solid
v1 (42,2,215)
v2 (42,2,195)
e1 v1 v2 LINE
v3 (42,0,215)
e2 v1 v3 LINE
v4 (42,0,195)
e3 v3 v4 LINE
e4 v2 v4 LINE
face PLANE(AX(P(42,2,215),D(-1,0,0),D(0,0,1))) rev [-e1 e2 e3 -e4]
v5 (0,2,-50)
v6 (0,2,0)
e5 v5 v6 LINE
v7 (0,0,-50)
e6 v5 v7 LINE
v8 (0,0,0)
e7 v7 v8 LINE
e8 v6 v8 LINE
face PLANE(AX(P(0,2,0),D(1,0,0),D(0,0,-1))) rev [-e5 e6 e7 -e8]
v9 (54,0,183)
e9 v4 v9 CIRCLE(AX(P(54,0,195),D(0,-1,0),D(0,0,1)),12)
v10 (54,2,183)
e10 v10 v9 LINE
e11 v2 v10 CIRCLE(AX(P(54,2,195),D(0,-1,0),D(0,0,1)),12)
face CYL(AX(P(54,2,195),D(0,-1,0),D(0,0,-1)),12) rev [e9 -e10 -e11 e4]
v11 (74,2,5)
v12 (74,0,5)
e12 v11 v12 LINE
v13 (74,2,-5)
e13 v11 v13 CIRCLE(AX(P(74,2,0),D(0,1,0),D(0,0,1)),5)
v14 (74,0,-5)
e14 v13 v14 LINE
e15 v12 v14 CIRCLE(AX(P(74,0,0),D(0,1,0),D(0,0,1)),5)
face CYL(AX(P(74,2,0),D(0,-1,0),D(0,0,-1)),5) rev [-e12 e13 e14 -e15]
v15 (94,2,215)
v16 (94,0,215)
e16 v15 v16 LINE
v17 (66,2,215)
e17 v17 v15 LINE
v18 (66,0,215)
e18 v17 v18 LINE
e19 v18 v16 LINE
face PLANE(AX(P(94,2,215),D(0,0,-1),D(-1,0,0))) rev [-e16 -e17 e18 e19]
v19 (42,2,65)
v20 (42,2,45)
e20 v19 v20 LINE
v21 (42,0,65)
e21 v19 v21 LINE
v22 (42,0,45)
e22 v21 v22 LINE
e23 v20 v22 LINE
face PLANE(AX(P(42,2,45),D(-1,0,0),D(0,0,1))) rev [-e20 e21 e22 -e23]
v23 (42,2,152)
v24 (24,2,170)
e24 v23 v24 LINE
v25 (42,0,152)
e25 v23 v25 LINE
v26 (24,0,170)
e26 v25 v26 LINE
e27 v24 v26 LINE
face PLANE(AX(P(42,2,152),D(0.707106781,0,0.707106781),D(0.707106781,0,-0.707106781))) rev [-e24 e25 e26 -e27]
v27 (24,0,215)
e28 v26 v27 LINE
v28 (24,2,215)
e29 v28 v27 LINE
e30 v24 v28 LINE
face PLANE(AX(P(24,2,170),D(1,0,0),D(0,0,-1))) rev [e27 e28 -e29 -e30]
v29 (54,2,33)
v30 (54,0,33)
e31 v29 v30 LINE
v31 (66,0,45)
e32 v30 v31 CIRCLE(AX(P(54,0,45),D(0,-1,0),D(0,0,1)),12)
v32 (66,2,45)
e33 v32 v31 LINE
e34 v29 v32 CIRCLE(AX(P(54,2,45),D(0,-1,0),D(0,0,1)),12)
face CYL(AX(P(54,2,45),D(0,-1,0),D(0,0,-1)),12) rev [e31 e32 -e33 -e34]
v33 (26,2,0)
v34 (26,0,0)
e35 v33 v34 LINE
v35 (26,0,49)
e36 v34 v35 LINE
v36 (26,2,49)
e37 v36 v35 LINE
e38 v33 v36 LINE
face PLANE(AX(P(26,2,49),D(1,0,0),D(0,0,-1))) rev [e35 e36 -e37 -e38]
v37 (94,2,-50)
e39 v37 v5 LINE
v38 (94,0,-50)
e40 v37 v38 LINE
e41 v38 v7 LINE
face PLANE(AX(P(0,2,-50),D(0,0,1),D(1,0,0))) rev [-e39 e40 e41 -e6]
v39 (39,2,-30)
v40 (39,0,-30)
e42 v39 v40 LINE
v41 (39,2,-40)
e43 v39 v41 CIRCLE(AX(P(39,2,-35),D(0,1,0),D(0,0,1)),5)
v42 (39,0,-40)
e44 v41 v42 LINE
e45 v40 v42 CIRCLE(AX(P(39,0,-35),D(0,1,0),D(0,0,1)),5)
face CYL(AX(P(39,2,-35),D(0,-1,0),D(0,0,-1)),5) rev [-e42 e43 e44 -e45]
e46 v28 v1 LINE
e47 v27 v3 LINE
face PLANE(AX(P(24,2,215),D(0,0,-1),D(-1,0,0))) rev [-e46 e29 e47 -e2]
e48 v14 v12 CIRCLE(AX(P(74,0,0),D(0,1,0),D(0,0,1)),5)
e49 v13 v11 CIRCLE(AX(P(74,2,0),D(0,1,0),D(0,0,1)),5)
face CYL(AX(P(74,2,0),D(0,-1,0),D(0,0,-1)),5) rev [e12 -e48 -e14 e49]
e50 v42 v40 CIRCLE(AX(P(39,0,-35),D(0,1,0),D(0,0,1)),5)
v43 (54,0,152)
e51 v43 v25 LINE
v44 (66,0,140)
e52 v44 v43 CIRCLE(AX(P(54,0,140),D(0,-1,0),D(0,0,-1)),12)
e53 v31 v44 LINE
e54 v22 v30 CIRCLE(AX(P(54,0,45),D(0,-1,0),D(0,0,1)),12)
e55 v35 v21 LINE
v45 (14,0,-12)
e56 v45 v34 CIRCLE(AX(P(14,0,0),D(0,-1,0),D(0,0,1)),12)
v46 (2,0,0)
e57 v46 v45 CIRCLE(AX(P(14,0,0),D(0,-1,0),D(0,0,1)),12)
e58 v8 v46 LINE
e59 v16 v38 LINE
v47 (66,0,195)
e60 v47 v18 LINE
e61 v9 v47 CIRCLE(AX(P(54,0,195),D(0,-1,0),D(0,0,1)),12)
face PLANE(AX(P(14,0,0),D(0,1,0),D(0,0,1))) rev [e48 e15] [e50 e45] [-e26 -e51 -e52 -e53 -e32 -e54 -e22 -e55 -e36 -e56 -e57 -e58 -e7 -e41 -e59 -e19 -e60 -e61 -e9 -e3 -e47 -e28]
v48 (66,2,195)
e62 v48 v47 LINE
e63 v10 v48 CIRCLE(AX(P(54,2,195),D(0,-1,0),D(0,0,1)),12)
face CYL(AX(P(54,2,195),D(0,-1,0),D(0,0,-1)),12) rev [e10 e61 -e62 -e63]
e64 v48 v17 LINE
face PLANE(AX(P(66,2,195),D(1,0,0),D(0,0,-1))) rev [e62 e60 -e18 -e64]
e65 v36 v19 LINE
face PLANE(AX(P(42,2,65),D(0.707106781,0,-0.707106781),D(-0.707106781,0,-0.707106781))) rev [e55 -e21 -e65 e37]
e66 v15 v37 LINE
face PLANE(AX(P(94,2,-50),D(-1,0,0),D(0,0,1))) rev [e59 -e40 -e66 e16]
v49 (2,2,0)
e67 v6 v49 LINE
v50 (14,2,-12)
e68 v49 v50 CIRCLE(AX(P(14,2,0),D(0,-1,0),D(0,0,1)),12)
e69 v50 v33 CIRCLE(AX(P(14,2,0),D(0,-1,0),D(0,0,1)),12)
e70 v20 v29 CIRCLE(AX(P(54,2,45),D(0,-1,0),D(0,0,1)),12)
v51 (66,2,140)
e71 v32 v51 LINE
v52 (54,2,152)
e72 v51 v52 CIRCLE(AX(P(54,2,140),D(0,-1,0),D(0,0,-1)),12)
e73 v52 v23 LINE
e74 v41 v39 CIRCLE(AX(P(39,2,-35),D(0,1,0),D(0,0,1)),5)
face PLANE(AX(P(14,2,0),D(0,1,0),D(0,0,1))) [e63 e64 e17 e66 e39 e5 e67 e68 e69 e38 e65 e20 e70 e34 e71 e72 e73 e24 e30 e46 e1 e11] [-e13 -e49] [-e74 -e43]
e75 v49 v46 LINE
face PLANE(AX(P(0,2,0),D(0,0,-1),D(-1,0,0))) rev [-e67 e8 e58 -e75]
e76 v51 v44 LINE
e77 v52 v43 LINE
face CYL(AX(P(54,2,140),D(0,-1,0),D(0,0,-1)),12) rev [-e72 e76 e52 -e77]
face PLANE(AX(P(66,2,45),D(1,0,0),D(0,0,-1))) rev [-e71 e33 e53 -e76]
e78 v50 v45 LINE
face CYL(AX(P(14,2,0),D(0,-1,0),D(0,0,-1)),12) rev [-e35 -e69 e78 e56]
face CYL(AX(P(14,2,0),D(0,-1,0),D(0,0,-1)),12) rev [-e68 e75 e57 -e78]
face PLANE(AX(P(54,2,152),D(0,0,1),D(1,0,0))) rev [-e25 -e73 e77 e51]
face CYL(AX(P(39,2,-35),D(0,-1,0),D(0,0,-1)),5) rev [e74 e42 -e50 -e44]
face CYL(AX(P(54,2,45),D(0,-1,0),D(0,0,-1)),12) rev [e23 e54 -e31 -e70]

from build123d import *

# Parameters (mm, degrees)
SKETCH_1_R      = 5
EXTRUDE_1_DEPTH = 2


with BuildPart() as part:
    # 草图1 → 凸台-拉伸1 (new body)
    with BuildSketch(Plane(origin=(0, 0, 0), x_dir=(1, 0, 0), z_dir=(0, 1, 0))):
        with BuildLine():
            Line((0, 0), (0, 50))
            Line((0, 50), (94, 50))
            Line((94, 50), (94, -215))
            Line((94, -215), (66, -215))
            Line((66, -215), (66, -195))
            ThreePointArc((66, -195), (54, -183), (42, -195))
            Line((42, -195), (42, -215))
            Line((42, -215), (24, -215))
            Line((24, -215), (24, -170))
            Line((24, -170), (42, -152))
            Line((42, -152), (54, -152))
            ThreePointArc((54, -152), (62.485281374, -148.485281374), (66, -140))
            Line((66, -140), (66, -45))
            ThreePointArc((66, -45), (54, -33), (42, -45))
            Line((42, -45), (42, -65))
            Line((42, -65), (26, -49))
            Line((26, -49), (26, 0))
            ThreePointArc((26, 0), (14, 12), (2, 0))
            Line((2, 0), (0, 0))
        make_face()
        with Locations(Location((39, 35, 0), (0, 0, 90))):
            Circle(SKETCH_1_R, mode=Mode.SUBTRACT)
        with Locations(Location((74, 0, 0), (0, 0, 90))):
            Circle(SKETCH_1_R, mode=Mode.SUBTRACT)
    extrude(amount=EXTRUDE_1_DEPTH)


solid = part.part
